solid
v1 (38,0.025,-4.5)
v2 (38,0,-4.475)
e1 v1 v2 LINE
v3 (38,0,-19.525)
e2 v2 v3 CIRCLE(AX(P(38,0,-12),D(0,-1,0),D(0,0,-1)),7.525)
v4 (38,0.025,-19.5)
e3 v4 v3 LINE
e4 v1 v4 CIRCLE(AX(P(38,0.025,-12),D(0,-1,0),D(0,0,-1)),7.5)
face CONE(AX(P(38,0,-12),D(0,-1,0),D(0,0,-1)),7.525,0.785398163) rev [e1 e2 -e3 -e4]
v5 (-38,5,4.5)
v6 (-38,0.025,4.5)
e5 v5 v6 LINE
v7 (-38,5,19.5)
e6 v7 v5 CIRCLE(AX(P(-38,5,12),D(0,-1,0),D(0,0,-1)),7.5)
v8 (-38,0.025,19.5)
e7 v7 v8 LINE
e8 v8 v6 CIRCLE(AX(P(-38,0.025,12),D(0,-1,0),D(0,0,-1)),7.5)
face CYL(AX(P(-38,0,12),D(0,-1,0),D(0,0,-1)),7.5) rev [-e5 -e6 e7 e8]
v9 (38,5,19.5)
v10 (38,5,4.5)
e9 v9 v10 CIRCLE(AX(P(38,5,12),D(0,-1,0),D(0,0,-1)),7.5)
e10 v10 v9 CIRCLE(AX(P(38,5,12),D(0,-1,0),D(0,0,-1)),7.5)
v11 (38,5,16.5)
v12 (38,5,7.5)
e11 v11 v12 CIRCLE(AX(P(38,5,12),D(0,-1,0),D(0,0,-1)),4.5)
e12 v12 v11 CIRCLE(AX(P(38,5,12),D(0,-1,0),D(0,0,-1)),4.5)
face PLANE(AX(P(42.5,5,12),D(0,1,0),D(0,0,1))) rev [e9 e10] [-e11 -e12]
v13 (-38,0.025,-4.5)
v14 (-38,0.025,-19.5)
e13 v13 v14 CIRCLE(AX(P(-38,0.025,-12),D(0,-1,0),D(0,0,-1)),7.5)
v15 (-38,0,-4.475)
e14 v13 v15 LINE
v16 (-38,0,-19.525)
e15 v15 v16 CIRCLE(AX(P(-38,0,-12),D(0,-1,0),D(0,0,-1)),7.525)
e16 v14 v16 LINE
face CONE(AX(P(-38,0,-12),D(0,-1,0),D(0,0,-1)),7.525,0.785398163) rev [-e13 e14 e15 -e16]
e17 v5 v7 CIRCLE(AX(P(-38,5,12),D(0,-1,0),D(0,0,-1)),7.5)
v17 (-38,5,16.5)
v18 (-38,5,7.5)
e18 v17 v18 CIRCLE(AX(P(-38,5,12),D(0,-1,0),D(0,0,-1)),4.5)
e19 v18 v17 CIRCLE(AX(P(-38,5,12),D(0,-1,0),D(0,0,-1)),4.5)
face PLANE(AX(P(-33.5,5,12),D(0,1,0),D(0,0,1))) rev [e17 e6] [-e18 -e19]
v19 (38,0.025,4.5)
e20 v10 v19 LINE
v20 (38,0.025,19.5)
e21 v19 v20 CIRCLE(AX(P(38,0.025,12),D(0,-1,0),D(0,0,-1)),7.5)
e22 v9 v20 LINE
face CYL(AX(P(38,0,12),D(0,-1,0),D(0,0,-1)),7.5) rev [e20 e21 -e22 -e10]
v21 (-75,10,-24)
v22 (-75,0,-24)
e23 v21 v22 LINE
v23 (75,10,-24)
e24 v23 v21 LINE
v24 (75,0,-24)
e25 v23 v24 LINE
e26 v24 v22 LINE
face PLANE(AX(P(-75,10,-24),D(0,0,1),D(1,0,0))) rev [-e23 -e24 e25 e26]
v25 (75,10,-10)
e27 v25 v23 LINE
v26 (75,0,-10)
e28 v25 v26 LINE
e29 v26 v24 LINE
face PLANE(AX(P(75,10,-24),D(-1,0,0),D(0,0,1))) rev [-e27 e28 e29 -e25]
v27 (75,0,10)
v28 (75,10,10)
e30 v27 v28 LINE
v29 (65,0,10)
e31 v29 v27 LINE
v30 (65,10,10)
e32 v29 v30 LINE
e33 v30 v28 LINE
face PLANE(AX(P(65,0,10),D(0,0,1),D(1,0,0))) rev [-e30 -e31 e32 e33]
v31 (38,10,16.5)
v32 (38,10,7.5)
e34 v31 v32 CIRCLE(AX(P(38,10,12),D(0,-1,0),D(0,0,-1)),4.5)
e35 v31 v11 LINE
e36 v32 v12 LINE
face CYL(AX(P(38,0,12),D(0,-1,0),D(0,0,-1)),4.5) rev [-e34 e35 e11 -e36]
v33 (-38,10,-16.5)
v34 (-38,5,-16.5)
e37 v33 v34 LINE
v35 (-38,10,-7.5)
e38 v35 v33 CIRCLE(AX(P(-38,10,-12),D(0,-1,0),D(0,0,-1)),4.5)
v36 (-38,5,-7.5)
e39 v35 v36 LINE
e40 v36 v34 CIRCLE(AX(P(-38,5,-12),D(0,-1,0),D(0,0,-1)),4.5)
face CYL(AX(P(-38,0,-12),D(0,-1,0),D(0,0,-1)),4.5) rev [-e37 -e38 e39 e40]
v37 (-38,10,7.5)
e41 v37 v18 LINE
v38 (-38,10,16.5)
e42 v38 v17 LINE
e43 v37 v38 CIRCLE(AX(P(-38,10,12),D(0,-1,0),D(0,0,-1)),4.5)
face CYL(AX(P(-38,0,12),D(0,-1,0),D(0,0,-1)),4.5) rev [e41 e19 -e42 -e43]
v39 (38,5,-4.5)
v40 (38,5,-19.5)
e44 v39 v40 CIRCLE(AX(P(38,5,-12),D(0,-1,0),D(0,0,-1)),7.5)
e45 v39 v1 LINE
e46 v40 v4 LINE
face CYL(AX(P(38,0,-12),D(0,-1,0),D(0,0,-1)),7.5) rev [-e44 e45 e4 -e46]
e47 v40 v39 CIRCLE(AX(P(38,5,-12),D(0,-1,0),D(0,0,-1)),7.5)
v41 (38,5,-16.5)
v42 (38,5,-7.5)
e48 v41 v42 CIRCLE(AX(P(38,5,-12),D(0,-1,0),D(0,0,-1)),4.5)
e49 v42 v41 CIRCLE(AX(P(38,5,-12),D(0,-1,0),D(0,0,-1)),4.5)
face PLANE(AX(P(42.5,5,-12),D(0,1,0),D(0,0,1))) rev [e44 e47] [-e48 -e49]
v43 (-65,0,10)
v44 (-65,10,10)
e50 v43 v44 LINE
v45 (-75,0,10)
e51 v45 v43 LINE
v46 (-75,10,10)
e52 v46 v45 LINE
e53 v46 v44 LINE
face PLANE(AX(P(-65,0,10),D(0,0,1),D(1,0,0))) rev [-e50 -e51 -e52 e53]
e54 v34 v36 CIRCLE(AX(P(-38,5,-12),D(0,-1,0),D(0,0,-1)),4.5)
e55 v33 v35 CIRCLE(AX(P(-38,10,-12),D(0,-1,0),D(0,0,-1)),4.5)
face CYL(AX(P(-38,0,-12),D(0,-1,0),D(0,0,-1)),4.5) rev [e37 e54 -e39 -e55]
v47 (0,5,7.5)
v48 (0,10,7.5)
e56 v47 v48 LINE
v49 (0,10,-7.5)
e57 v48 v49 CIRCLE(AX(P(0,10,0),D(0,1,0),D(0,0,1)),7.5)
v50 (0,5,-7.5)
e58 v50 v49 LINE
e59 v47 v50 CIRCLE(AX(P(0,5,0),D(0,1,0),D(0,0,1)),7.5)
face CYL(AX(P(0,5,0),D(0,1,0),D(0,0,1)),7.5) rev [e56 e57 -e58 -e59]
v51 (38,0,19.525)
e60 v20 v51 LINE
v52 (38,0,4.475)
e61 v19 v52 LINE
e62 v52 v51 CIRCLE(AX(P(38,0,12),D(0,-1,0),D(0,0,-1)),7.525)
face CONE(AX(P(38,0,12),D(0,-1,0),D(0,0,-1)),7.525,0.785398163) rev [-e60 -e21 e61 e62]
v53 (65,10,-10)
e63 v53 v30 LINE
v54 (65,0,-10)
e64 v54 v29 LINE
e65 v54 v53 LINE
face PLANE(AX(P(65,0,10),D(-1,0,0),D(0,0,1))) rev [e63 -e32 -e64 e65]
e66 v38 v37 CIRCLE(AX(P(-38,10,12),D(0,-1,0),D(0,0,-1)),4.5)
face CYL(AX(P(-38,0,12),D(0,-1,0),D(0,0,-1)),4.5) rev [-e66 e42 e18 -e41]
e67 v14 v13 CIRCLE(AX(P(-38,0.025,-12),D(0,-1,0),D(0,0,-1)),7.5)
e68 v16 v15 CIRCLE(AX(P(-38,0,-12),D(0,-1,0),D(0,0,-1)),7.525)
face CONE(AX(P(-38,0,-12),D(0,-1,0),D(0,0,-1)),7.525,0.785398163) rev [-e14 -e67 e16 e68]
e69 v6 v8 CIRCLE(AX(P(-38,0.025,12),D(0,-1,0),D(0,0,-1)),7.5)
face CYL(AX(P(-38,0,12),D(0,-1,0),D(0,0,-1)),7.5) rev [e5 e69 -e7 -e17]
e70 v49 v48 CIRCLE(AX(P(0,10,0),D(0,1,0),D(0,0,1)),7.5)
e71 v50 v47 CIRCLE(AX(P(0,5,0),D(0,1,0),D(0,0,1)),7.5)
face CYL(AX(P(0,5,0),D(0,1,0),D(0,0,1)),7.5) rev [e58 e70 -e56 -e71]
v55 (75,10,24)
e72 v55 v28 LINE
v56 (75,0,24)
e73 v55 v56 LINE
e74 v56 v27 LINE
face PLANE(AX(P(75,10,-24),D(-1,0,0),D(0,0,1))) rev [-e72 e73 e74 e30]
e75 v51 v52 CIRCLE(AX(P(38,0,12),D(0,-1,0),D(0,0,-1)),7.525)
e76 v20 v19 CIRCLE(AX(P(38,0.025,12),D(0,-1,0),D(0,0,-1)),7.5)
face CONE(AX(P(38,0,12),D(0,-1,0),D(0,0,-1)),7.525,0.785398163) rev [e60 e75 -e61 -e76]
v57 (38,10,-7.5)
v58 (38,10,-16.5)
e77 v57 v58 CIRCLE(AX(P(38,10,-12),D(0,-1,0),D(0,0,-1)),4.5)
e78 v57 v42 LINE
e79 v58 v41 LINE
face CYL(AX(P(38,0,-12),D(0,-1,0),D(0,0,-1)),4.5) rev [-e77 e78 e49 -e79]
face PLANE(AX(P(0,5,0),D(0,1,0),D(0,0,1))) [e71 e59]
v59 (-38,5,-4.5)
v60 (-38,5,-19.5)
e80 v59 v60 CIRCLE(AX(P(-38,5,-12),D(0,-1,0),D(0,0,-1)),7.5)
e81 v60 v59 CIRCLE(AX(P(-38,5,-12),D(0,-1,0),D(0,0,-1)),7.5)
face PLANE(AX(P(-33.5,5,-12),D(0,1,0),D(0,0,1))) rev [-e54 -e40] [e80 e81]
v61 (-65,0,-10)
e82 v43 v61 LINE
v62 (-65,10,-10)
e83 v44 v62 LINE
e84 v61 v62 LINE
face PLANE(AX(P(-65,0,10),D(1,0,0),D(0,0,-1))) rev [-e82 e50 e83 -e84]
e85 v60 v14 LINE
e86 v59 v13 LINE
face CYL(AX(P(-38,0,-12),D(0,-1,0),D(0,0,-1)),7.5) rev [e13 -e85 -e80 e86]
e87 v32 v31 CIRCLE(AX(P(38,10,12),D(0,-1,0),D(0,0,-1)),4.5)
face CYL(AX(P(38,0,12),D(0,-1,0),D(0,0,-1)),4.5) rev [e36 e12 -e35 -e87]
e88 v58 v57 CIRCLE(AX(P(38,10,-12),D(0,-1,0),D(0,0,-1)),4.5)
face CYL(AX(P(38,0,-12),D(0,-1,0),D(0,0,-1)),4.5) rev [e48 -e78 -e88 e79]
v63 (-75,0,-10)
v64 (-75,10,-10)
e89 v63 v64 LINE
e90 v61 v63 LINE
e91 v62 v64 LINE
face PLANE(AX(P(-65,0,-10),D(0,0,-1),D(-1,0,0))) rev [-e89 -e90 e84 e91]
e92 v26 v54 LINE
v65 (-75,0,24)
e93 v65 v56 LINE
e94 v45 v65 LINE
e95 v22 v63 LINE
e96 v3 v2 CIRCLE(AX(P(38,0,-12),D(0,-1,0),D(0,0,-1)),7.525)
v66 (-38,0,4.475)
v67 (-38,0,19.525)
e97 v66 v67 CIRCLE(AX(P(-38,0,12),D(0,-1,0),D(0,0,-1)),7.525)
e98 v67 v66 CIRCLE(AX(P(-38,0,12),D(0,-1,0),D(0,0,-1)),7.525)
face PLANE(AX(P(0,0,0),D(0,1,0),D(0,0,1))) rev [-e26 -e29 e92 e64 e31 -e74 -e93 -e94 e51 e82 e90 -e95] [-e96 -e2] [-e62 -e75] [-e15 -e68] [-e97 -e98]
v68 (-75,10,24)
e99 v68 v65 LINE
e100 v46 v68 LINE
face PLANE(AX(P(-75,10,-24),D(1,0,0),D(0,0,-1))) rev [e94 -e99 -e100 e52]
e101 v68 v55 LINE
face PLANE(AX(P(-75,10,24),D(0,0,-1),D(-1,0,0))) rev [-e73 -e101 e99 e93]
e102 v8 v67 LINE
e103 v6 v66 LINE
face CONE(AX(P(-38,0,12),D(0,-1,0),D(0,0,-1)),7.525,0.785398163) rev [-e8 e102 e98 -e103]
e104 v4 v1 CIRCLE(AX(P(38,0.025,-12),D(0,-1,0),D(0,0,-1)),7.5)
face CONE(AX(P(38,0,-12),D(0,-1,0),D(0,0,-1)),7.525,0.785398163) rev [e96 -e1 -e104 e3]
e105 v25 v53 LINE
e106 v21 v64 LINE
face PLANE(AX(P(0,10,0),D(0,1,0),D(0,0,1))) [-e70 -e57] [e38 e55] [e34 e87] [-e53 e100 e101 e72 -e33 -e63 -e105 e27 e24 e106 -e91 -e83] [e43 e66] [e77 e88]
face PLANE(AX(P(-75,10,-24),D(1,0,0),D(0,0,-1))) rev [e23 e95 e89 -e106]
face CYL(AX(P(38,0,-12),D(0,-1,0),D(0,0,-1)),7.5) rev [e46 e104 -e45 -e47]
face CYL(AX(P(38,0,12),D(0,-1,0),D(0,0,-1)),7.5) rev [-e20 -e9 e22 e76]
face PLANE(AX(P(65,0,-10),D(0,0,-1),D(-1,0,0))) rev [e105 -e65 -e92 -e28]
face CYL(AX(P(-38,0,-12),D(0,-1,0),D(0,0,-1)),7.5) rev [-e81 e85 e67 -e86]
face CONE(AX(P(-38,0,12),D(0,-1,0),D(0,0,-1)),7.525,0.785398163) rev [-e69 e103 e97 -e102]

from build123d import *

# Parameters (mm, degrees)
SKETCH1_W                                  = 150
SKETCH1_H                                  = 48
BOSS_EXTRUDE1_DEPTH                        = 10
CBORE_FOR_M8_CHEESE_HEAD_SCREW1_AT_2_COUNT = 2
CBORE_FOR_M8_CHEESE_HEAD_SCREW1_AT_2_PITCH = 76
CBORE_FOR_M8_CHEESE_HEAD_SCREW1_AT_3_COUNT = 2
CBORE_FOR_M8_CHEESE_HEAD_SCREW1_AT_3_PITCH = 24
CBORE_FOR_M8_CHEESE_HEAD_SCREW1_AT_4_COUNT = 2
CBORE_FOR_M8_CHEESE_HEAD_SCREW1_AT_4_PITCH = 79.699435381
SKETCH6_R                                  = 7.5
CUT_EXTRUDE2_DEPTH                         = 5
SKETCH7_W                                  = 20
SKETCH7_H                                  = 20
CUT_EXTRUDE3_DEPTH                         = 80.37883849


with BuildPart() as part:
    # Sketch1 → Boss-Extrude1 (new body)
    with BuildSketch(Plane(origin=(0, 0, 0), x_dir=(1, 0, 0), z_dir=(0, 1, 0))):
        Rectangle(SKETCH1_W, SKETCH1_H)
    extrude(amount=BOSS_EXTRUDE1_DEPTH)

    # Sketch4 → CBORE for M8 Cheese Head Screw1 (revolve, cut)
    with BuildSketch(Plane(origin=(38, 0, 12), x_dir=(0, 0, -1), z_dir=(1, 0, 0))):
        Polygon((0, 0), (0, 12.703872786), (4.5, 10), (4.5, 5), (7.5, 5), (7.5, 0.025), (7.525, 0), align=None)
    cbore_for_m8_cheese_head_screw1 = revolve(axis=Axis((38, -6.35, 12), (0, 1, 0)), mode=Mode.SUBTRACT)

    # CBORE for M8 Cheese Head Screw1 at 2: CBORE for M8 Cheese Head Screw1 ×2
    with Locations(*[(-i * CBORE_FOR_M8_CHEESE_HEAD_SCREW1_AT_2_PITCH, 0, 0) for i in range(1, CBORE_FOR_M8_CHEESE_HEAD_SCREW1_AT_2_COUNT)]):
        add(cbore_for_m8_cheese_head_screw1, mode=Mode.SUBTRACT)

    # CBORE for M8 Cheese Head Screw1 at 3: CBORE for M8 Cheese Head Screw1 ×2
    with Locations(*[(0, 0, -i * CBORE_FOR_M8_CHEESE_HEAD_SCREW1_AT_3_PITCH) for i in range(1, CBORE_FOR_M8_CHEESE_HEAD_SCREW1_AT_3_COUNT)]):
        add(cbore_for_m8_cheese_head_screw1, mode=Mode.SUBTRACT)

    # CBORE for M8 Cheese Head Screw1 at 4: CBORE for M8 Cheese Head Screw1 ×2
    with Locations(*[Vector(-0.9535826651341417, 0, -0.3011313679370974) * (i * CBORE_FOR_M8_CHEESE_HEAD_SCREW1_AT_4_PITCH) for i in range(1, CBORE_FOR_M8_CHEESE_HEAD_SCREW1_AT_4_COUNT)]):
        add(cbore_for_m8_cheese_head_screw1, mode=Mode.SUBTRACT)

    # Sketch6 → Cut-Extrude2 (cut)
    with BuildSketch(Plane(origin=(0, 10, 0), x_dir=(1, 0, 0), z_dir=(0, 1, 0))):
        with Locations(Location((0, 0, 0), (0, 0, 270))):
            Circle(SKETCH6_R)
    extrude(amount=-CUT_EXTRUDE2_DEPTH, mode=Mode.SUBTRACT)

    # Sketch7 → Cut-Extrude3 (cut, through all)
    with BuildSketch(Plane(origin=(0, 10, 0), x_dir=(1, 0, 0), z_dir=(0, 1, 0))):
        with Locations((75, 0)):
            Rectangle(SKETCH7_W, SKETCH7_H)
        with Locations((-75, 0)):
            Rectangle(SKETCH7_W, SKETCH7_H)
    extrude(amount=-CUT_EXTRUDE3_DEPTH, mode=Mode.SUBTRACT)


solid = part.part
